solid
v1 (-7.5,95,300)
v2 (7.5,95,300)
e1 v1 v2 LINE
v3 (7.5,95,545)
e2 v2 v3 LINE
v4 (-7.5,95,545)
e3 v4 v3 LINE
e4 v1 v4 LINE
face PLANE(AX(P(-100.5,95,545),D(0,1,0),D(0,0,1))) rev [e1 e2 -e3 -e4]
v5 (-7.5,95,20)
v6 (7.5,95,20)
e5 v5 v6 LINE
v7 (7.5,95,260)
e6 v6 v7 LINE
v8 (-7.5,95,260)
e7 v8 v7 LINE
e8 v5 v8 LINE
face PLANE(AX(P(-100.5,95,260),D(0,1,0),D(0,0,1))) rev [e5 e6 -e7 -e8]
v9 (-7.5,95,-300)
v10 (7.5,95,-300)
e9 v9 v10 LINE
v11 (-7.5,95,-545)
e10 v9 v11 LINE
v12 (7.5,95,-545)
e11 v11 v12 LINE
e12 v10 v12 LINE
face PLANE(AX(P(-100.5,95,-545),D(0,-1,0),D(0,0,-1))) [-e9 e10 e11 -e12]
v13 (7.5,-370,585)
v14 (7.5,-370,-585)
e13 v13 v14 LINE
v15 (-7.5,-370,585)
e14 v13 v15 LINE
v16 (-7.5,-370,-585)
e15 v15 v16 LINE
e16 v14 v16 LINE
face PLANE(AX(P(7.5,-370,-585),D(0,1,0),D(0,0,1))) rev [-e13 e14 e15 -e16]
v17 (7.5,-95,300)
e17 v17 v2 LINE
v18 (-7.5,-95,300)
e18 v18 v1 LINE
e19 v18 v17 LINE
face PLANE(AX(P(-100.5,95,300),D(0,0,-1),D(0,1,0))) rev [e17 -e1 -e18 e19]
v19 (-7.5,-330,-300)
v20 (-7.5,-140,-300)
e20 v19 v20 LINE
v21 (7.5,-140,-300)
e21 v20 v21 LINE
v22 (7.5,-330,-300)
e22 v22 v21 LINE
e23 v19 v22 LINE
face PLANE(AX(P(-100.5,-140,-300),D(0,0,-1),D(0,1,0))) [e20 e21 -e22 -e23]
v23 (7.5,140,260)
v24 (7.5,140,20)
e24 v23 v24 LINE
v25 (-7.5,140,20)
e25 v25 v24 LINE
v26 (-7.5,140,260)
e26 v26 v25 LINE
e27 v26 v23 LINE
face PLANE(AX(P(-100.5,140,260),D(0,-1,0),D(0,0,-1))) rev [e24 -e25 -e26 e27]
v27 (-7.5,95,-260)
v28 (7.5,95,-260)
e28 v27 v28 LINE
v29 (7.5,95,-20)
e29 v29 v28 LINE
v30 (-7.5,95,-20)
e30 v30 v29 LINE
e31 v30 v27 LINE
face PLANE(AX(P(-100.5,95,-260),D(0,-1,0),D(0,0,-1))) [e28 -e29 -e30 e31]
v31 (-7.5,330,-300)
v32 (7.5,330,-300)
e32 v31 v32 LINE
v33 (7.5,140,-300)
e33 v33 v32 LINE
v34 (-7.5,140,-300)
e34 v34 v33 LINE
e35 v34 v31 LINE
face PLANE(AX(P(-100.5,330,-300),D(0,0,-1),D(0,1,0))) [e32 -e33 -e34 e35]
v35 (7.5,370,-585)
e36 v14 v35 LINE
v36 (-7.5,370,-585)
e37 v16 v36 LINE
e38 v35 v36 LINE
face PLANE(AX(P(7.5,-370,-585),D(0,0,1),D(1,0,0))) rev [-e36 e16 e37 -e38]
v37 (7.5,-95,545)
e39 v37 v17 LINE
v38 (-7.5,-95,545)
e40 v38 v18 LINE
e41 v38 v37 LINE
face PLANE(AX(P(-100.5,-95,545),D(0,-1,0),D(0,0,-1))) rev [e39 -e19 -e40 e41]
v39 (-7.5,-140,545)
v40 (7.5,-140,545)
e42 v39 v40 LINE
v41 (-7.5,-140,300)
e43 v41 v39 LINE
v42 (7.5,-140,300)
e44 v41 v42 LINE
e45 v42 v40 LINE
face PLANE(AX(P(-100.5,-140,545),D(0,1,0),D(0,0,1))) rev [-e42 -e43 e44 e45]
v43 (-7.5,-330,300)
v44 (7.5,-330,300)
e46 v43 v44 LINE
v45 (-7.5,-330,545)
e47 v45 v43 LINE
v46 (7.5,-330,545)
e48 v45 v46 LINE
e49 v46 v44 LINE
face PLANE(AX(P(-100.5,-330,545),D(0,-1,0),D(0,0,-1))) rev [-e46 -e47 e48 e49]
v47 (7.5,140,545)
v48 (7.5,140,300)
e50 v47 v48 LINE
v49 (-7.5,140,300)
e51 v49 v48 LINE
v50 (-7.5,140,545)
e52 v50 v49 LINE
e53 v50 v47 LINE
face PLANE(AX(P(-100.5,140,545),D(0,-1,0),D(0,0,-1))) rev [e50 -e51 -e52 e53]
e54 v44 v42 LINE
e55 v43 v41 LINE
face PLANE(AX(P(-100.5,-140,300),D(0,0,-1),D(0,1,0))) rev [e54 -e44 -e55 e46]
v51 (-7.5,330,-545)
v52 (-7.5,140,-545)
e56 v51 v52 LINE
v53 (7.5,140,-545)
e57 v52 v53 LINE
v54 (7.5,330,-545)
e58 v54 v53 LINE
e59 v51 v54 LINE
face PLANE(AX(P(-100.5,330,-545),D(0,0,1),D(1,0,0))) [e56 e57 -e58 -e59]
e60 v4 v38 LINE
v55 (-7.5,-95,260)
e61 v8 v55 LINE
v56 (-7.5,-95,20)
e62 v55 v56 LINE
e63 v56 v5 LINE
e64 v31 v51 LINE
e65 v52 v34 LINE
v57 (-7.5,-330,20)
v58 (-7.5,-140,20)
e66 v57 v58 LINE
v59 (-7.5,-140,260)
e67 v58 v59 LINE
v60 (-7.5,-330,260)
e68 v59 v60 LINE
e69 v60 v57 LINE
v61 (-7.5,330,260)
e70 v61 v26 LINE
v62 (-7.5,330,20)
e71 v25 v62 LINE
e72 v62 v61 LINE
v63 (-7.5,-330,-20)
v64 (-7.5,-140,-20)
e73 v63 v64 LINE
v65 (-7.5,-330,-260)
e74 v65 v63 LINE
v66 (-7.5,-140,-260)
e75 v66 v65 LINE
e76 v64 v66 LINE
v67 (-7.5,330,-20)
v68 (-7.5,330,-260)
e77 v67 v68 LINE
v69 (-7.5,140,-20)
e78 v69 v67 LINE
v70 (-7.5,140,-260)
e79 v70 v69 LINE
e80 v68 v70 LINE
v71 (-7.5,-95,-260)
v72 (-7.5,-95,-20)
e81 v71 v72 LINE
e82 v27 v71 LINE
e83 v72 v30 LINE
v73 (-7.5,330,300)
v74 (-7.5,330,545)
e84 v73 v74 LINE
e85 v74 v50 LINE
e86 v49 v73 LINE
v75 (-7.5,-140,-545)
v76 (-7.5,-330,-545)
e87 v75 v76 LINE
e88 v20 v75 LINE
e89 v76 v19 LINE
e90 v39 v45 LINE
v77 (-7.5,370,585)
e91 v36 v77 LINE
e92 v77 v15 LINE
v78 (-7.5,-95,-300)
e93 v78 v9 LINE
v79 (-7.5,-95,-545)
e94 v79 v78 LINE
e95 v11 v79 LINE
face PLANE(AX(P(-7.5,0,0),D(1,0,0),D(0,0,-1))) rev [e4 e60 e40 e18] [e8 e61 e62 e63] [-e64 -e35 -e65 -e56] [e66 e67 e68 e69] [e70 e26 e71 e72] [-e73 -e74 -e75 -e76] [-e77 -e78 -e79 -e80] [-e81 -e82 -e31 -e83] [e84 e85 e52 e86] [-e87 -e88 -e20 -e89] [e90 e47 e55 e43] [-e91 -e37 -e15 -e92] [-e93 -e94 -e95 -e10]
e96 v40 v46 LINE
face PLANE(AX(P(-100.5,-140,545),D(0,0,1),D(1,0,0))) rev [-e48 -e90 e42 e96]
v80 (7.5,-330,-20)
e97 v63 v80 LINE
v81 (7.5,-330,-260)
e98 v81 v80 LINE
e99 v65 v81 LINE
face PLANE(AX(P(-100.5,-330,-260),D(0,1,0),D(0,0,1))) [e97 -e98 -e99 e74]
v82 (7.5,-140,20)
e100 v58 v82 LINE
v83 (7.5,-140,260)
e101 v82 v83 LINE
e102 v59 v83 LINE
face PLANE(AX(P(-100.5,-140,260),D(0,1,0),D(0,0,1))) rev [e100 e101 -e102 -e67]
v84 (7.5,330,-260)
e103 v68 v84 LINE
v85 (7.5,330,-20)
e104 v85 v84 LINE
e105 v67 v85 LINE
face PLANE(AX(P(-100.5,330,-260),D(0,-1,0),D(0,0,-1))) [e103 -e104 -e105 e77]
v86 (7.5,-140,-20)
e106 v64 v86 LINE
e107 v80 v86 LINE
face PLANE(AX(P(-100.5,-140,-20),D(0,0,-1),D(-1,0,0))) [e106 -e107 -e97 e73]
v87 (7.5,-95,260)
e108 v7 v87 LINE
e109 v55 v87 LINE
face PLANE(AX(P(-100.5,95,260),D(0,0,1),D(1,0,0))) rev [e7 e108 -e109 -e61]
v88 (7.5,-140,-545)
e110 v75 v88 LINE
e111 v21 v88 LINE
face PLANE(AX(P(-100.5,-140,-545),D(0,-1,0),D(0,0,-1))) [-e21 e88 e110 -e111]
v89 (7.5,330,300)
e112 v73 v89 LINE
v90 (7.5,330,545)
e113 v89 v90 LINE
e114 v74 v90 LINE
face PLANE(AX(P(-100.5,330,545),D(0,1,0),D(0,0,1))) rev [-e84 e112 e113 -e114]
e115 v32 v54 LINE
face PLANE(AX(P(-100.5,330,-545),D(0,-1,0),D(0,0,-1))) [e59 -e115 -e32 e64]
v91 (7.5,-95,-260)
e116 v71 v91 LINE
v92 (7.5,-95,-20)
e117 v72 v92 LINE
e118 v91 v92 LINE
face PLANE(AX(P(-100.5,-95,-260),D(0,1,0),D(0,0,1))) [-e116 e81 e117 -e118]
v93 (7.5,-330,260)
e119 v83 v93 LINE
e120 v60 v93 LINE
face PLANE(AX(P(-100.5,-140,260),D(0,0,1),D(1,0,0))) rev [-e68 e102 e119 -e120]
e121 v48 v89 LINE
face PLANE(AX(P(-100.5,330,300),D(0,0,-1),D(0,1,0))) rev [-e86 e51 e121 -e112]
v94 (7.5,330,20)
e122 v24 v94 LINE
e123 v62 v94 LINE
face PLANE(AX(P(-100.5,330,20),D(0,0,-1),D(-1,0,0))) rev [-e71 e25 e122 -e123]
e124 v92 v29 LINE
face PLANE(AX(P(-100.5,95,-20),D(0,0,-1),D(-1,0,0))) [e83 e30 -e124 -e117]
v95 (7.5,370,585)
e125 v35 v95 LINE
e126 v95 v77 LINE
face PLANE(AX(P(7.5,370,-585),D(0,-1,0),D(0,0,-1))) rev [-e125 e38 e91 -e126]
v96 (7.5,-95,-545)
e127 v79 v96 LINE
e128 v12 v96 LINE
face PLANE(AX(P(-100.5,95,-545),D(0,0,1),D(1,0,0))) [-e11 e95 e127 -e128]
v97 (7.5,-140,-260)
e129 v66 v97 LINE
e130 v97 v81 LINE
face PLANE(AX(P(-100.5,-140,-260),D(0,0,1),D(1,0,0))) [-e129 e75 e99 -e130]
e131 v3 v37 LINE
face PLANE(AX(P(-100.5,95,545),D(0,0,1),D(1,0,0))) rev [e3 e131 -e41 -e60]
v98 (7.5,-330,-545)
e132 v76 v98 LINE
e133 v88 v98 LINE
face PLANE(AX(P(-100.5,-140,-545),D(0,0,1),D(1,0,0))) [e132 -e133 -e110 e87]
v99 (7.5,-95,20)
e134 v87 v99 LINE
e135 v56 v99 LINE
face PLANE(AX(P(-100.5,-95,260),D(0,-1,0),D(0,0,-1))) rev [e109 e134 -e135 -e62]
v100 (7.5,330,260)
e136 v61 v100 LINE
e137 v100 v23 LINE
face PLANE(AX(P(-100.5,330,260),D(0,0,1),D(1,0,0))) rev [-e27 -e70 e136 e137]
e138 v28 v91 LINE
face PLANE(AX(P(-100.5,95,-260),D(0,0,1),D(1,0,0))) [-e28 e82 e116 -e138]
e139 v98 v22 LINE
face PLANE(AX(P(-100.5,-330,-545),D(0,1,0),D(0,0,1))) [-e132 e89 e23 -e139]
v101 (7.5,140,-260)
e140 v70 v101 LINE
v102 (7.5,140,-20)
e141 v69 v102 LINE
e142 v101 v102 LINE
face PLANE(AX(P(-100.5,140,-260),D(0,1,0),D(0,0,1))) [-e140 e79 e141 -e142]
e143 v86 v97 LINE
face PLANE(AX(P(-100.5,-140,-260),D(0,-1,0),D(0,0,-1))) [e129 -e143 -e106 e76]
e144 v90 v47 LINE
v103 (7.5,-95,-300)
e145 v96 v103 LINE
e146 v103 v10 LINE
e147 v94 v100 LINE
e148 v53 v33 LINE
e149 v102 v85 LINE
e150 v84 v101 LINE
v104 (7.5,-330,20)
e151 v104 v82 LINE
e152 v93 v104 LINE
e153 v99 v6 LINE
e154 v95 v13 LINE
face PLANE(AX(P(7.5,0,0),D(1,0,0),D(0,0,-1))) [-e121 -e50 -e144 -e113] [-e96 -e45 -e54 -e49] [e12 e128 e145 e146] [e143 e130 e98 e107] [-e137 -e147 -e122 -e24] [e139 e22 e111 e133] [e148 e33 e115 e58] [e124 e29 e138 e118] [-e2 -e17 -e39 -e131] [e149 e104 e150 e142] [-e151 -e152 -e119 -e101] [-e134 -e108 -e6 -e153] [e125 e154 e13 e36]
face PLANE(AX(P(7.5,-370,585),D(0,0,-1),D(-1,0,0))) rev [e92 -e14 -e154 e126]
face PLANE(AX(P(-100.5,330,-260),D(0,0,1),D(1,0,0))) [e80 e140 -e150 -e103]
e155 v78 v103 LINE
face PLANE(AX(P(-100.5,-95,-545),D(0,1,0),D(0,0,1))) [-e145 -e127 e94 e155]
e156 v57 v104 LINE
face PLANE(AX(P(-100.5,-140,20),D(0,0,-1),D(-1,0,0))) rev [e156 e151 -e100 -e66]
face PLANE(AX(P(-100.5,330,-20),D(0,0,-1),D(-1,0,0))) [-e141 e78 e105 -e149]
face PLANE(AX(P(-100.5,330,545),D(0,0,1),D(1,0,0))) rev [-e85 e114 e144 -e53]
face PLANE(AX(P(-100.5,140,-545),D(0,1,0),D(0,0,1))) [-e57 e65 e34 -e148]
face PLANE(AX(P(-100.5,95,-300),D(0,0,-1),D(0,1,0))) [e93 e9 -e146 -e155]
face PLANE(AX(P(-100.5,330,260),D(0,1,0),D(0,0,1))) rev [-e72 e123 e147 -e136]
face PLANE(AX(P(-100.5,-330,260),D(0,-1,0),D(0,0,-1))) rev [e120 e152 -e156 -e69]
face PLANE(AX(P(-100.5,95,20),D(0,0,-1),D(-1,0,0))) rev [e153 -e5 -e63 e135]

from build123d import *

# Parameters (mm, degrees)
SKETCH1_W           = 1170
SKETCH1_H           = 740
BOSS_EXTRUDE1_DEPTH = 7.5
SKETCH2_W           = 245
SKETCH2_H           = 190
SKETCH2_W_2         = 240
CUT_EXTRUDE1_DEPTH  = 108


with BuildPart() as part:
    # Sketch1 → Boss-Extrude1 (new, symmetric)
    with BuildSketch(Plane(origin=(0, 0, 0), x_dir=(0, 0, -1), z_dir=(1, 0, 0))):
        Rectangle(SKETCH1_W, SKETCH1_H)
    extrude(amount=BOSS_EXTRUDE1_DEPTH, both=True)

    # Sketch2 → Cut-Extrude1 (cut)
    with BuildSketch(Plane(origin=(7.5, 0, 0), x_dir=(0, 0, -1), z_dir=(1, 0, 0))):
        with Locations((-422.5, 235)):
            Rectangle(SKETCH2_W, SKETCH2_H)
        with Locations((-422.5, 0)):
            Rectangle(SKETCH2_W, SKETCH2_H)
        with Locations((-140, 0)):
            Rectangle(SKETCH2_W_2, SKETCH2_H)
        with Locations((-140, 235)):
            Rectangle(SKETCH2_W_2, SKETCH2_H)
        with Locations((-422.5, -235)):
            Rectangle(SKETCH2_W, SKETCH2_H)
        with Locations((-140, -235)):
            Rectangle(SKETCH2_W_2, SKETCH2_H)
    cut_extrude1 = extrude(amount=-CUT_EXTRUDE1_DEPTH, mode=Mode.SUBTRACT)

    # Mirror1: Cut-Extrude1 across plane
    add(cut_extrude1.mirror(Plane.XY), mode=Mode.SUBTRACT)


solid = part.part
